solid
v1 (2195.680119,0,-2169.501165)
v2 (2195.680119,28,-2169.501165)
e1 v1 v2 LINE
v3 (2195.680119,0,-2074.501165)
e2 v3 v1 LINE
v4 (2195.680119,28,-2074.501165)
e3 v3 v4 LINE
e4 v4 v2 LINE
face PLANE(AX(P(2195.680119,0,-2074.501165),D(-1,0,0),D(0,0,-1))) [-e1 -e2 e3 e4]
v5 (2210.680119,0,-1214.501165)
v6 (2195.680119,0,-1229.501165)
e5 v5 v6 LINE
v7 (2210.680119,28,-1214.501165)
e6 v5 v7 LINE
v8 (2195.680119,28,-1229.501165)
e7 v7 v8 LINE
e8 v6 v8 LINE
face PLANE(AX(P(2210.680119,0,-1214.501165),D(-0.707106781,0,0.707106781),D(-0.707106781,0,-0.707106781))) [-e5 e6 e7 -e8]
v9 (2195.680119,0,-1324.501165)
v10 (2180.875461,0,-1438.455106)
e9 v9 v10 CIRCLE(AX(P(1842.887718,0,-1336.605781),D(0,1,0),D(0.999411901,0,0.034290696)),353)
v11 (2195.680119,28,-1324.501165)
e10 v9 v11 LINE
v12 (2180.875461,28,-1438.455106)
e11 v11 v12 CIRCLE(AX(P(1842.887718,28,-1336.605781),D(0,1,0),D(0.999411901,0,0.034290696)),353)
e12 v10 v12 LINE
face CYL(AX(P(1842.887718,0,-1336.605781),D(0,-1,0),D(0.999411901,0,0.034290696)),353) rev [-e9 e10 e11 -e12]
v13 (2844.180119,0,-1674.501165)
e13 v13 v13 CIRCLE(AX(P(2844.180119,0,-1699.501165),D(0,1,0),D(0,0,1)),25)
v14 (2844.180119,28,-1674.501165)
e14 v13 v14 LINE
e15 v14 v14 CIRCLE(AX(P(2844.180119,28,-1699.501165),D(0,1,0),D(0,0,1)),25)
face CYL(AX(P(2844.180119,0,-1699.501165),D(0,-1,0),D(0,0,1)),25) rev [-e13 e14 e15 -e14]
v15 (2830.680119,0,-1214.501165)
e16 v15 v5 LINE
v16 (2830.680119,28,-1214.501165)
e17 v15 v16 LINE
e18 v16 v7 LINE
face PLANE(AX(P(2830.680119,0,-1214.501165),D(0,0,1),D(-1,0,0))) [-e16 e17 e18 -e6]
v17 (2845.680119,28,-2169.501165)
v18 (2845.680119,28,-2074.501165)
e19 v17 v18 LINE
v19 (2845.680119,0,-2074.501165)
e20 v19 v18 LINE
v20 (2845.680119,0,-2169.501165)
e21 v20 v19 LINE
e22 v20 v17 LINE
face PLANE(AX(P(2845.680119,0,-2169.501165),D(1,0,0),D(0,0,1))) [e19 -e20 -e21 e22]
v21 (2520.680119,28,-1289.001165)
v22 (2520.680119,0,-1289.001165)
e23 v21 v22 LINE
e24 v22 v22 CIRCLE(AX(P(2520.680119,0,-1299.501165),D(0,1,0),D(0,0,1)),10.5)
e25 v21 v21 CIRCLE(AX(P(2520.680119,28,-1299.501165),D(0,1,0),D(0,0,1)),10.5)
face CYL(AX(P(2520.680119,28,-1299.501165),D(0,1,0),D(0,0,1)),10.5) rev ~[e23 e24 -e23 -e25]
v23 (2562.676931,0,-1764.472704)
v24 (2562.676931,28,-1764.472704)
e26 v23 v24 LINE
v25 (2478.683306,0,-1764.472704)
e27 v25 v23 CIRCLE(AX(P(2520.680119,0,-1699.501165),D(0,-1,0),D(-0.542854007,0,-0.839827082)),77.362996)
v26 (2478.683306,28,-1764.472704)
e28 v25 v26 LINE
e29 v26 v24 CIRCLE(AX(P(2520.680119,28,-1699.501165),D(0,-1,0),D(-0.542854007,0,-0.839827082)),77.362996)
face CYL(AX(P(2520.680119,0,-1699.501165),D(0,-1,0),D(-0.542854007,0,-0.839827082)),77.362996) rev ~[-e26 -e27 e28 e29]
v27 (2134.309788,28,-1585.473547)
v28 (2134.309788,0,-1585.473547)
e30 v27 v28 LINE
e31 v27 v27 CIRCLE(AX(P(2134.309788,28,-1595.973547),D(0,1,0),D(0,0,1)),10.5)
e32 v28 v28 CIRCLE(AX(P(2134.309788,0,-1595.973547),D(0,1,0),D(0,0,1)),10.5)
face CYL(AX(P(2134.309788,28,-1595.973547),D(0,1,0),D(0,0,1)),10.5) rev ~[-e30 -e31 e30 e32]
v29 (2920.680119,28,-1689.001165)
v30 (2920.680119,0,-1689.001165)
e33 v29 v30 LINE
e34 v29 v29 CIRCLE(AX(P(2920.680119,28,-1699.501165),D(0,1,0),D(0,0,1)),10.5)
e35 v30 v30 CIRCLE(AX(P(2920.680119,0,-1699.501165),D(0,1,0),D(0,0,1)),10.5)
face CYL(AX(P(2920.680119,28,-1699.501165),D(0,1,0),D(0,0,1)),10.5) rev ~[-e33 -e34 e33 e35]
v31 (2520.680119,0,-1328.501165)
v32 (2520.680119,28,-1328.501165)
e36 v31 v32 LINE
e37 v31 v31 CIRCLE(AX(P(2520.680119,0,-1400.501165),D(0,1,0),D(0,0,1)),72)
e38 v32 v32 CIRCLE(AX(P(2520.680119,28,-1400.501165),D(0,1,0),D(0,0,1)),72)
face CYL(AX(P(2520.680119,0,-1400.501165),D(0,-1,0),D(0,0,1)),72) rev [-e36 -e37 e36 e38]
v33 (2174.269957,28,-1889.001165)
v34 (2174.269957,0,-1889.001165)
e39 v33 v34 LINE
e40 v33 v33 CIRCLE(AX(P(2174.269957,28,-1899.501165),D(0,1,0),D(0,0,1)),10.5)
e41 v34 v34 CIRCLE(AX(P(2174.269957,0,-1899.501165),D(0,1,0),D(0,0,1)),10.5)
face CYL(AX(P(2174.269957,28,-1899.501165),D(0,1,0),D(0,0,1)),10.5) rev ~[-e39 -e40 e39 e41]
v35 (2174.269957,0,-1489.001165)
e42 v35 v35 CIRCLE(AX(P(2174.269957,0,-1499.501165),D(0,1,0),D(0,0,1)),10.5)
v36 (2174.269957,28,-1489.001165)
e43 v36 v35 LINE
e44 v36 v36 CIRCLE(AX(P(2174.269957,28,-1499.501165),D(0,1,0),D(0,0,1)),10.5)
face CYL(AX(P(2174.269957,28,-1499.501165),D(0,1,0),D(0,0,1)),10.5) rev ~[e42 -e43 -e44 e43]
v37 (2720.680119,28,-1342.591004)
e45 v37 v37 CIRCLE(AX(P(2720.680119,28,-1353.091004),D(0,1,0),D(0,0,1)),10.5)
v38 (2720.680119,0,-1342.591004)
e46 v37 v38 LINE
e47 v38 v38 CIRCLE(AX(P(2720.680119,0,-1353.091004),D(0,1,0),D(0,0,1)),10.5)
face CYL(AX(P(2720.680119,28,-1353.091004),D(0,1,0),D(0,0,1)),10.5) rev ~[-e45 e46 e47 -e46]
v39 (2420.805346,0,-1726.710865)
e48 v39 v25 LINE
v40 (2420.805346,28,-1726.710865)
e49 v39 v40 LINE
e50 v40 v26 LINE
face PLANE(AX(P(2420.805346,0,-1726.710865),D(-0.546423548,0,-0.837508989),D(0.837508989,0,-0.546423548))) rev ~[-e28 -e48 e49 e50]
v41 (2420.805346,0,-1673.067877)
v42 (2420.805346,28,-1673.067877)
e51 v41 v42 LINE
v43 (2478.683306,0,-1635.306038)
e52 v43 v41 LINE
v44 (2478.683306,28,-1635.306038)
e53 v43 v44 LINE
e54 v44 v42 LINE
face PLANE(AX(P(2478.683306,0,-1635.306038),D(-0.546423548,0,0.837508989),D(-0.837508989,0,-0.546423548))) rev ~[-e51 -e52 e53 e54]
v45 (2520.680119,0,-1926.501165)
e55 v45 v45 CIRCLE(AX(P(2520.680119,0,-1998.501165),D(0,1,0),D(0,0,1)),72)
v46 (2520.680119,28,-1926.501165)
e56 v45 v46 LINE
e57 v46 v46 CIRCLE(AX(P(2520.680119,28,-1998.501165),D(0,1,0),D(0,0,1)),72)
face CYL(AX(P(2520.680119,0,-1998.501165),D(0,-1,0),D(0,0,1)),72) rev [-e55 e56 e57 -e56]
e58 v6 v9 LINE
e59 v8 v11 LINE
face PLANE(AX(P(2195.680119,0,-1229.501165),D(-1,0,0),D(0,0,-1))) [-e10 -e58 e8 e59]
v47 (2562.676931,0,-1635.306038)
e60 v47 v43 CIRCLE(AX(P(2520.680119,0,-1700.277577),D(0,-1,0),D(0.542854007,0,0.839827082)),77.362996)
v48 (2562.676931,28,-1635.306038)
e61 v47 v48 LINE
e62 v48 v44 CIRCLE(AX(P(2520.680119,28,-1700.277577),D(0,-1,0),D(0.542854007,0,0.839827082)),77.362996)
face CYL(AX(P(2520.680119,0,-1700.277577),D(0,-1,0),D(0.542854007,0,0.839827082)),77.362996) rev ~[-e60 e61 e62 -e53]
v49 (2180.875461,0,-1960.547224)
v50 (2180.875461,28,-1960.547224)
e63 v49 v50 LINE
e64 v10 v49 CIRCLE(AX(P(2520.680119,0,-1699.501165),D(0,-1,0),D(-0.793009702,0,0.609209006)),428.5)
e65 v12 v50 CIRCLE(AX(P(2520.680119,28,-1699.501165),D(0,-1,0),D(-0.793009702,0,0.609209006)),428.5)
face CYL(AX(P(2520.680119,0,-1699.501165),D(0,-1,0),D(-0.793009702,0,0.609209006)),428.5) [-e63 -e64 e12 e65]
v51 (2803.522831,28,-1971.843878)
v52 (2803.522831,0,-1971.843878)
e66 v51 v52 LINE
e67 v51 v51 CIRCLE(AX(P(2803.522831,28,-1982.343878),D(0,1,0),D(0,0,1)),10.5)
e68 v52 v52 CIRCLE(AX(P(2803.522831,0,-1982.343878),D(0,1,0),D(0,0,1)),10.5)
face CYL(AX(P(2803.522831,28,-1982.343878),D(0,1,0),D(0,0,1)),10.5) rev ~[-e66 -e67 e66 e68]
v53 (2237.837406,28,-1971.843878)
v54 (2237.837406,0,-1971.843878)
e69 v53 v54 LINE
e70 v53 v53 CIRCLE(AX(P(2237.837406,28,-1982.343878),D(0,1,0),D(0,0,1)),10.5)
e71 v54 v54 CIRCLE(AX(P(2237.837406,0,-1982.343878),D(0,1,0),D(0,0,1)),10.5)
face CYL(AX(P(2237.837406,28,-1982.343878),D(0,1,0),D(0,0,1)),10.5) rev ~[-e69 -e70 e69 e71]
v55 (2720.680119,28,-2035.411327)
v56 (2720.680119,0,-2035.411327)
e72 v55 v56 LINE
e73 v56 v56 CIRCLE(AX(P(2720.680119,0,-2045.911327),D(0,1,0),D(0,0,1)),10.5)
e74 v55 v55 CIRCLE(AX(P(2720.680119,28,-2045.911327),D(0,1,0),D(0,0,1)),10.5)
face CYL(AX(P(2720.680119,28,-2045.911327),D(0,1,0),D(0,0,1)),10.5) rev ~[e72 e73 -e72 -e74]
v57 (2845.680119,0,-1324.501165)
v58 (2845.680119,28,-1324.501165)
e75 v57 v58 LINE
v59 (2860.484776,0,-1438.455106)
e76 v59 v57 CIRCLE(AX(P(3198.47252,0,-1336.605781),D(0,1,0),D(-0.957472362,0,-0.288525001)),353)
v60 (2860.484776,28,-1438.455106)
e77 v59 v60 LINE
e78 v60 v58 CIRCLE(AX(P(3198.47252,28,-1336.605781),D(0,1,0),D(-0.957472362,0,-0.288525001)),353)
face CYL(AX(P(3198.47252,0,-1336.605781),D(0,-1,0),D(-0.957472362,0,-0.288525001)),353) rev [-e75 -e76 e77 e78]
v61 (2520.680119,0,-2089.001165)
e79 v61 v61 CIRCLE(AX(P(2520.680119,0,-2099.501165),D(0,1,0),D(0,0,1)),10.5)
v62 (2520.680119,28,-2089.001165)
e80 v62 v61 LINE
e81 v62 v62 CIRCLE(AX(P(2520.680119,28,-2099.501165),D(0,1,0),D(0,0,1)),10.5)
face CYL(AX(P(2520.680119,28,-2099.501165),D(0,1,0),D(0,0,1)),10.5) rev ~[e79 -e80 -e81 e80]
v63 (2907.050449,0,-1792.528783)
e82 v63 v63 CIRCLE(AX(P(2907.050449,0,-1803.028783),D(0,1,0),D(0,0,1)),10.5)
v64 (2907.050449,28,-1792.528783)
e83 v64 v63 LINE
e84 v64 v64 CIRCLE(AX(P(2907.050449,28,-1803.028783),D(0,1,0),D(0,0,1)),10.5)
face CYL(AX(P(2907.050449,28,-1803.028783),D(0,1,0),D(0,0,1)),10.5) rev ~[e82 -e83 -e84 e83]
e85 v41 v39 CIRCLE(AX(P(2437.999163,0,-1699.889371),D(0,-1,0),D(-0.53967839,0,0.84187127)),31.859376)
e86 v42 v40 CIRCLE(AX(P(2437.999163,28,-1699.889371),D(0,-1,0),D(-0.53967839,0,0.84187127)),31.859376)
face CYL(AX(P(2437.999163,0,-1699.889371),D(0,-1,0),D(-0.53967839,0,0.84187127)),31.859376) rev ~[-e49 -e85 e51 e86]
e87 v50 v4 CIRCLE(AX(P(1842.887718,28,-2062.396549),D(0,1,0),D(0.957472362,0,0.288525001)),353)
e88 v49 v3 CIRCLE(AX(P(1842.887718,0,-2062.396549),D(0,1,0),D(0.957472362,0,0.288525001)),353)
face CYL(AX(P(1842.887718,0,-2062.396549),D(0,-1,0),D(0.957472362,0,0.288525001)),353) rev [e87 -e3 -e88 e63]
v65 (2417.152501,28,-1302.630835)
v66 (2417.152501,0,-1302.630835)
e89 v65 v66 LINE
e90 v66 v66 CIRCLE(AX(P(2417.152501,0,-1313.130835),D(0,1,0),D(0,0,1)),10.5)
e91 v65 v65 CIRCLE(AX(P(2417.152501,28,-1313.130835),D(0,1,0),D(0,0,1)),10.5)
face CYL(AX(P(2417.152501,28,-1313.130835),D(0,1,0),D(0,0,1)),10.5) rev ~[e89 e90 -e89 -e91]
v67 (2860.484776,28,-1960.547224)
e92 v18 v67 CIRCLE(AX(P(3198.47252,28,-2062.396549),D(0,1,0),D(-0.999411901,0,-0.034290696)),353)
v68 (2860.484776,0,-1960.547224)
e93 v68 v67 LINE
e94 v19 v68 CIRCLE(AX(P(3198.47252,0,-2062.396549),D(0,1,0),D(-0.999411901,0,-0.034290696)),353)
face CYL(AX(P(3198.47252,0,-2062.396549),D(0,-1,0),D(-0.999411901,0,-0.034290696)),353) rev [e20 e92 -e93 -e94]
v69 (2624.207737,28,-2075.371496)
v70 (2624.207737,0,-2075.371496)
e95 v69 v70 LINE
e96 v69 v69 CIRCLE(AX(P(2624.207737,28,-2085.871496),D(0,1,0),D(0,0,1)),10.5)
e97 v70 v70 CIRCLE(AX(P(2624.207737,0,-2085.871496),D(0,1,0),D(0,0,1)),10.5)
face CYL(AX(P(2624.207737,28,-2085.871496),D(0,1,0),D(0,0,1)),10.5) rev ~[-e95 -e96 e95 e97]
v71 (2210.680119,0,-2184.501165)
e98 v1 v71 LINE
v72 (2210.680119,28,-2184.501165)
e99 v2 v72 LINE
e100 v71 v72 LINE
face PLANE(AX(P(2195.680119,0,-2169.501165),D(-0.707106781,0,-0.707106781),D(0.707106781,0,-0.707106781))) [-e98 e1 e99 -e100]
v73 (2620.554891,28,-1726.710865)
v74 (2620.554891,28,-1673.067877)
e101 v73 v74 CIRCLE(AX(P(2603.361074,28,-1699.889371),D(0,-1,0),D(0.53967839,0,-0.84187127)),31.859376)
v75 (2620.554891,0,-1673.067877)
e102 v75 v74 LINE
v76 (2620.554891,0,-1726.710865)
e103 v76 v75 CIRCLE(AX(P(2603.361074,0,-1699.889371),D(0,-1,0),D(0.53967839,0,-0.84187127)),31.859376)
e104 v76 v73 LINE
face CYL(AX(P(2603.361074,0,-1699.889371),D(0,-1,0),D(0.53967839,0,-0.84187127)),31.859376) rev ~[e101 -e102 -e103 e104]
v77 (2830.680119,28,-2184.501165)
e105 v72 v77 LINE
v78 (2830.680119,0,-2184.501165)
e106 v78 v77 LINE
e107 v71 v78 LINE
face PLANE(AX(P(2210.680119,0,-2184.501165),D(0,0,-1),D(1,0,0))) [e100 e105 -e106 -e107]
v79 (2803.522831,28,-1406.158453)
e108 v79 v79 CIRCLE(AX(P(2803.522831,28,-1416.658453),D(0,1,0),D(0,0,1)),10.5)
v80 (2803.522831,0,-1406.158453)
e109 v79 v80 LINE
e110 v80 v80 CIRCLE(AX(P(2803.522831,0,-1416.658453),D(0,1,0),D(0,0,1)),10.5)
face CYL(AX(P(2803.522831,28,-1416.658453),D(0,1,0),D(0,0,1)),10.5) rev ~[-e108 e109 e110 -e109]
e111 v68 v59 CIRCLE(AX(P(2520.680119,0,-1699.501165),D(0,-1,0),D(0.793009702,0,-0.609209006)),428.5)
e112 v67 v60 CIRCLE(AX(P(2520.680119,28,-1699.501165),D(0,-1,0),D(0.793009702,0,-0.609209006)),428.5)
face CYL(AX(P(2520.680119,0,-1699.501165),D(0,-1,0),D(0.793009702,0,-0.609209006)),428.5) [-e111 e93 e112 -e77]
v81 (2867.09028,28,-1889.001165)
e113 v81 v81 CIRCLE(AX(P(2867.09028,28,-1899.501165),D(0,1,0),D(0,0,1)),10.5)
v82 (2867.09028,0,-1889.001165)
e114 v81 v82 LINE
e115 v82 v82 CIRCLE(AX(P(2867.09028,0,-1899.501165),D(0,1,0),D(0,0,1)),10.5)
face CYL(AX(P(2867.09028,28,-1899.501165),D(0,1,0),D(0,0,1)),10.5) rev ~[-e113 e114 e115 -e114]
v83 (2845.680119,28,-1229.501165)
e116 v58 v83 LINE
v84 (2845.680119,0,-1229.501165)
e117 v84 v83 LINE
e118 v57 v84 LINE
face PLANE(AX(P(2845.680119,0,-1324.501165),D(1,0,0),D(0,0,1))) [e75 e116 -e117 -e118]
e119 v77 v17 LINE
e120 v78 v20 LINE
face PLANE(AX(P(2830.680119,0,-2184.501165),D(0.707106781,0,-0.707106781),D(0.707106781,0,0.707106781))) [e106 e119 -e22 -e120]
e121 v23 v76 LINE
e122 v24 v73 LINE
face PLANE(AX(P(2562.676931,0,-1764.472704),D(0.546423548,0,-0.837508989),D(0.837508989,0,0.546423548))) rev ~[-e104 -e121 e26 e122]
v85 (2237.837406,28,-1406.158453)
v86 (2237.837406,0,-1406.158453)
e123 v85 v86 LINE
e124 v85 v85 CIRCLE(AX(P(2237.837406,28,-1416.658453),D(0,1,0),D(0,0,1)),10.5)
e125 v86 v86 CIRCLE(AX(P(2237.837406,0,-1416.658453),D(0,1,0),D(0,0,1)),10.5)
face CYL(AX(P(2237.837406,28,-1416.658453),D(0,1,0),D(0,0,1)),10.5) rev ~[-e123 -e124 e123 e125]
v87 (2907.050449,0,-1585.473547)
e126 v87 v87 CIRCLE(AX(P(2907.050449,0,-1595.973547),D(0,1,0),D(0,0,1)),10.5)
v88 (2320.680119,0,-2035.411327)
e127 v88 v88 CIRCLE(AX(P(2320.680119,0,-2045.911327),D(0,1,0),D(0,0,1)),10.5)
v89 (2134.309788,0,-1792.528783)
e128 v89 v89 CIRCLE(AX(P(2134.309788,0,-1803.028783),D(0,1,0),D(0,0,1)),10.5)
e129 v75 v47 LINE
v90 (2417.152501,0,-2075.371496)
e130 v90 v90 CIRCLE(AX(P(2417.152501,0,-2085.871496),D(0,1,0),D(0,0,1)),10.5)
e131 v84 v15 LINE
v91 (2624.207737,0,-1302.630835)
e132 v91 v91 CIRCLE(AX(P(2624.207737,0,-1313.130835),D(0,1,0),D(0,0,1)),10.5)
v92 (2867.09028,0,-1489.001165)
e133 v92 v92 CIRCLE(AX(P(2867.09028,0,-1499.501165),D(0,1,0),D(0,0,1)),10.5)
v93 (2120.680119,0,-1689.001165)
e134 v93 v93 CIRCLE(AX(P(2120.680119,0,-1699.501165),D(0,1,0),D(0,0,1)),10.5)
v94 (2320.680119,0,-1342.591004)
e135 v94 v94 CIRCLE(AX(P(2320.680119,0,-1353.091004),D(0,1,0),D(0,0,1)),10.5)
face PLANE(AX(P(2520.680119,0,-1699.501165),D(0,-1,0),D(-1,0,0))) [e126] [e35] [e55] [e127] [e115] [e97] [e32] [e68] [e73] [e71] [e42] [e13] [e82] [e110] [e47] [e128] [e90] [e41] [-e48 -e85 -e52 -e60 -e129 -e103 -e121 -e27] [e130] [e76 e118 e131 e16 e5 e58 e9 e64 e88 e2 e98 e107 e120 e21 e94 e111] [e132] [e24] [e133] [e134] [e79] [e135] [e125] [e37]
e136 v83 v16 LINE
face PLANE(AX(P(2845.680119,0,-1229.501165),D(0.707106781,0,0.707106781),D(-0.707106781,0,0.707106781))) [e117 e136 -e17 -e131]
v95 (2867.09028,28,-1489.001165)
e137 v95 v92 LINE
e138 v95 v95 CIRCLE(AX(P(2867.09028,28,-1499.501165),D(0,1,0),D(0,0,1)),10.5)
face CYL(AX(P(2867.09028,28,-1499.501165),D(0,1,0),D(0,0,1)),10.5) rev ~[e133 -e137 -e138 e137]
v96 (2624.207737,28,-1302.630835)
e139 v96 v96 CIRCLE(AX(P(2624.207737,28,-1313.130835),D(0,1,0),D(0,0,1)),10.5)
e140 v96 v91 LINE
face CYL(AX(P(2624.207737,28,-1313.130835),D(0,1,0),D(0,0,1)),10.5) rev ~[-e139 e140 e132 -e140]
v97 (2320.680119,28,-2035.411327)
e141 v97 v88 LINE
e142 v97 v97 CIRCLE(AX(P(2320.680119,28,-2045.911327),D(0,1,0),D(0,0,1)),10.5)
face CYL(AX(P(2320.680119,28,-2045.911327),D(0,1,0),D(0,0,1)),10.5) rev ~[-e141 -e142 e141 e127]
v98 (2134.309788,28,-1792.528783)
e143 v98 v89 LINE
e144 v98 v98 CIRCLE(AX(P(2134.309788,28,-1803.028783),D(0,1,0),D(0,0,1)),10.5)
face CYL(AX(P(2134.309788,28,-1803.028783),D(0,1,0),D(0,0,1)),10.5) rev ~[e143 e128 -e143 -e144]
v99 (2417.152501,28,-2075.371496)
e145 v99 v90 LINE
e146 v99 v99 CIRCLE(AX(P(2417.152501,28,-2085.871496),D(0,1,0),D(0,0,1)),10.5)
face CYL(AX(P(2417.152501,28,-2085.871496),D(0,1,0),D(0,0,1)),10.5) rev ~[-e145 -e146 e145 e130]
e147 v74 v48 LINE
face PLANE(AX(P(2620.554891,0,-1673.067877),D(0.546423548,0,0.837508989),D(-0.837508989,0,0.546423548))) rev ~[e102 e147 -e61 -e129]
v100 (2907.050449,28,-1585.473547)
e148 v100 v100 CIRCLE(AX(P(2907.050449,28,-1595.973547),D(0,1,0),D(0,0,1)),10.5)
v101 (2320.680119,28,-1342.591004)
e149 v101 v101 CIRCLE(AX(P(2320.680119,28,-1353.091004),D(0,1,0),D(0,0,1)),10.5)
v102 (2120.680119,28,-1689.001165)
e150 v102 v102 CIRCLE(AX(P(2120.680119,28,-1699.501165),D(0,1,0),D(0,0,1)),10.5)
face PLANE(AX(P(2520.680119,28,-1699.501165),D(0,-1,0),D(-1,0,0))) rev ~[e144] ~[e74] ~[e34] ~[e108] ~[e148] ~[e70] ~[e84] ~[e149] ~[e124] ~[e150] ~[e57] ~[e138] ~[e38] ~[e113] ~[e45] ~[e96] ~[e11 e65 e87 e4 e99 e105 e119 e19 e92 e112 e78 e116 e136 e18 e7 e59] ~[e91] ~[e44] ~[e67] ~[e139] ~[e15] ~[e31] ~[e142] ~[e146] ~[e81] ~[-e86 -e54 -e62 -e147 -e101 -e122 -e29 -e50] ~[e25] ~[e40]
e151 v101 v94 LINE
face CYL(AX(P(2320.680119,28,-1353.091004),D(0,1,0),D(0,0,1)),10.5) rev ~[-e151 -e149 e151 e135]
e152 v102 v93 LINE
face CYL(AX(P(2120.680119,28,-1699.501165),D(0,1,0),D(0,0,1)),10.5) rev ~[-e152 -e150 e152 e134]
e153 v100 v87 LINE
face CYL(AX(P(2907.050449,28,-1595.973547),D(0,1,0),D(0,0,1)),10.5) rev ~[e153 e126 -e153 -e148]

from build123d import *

# Parameters (mm, degrees)
SKETCH3_R           = 25
SKETCH3_R_2         = 72
BOSS_EXTRUDE1_DEPTH = 28
SKETCH4_R           = 10.5
CUT_EXTRUDE1_DEPTH  = 3671.216984417


with BuildPart() as part:
    # Sketch3 → Boss-Extrude1 (new body)
    with BuildSketch(Plane(origin=(0, 0, 0), x_dir=(1, 0, 0), z_dir=(0, 1, 0))):
        with BuildLine():
            Line((2845.680118699, 2169.501165066), (2845.680118699, 2074.501165066))
            ThreePointArc((2845.680118699, 2074.501165066), (2848.414414178, 2016.917733414), (2860.484776028, 1960.547223948))
            ThreePointArc((2860.484776028, 1960.547223948), (2949.180118699, 1699.501165066), (2860.484776028, 1438.455106185))
            ThreePointArc((2860.484776028, 1438.455106185), (2848.414414178, 1382.084596719), (2845.680118699, 1324.501165066))
            Line((2845.680118699, 1324.501165066), (2845.680118699, 1229.501165066))
            Line((2845.680118699, 1229.501165066), (2830.680118699, 1214.501165066))
            Line((2830.680118699, 1214.501165066), (2210.680118699, 1214.501165066))
            Line((2210.680118699, 1214.501165066), (2195.680118699, 1229.501165066))
            Line((2195.680118699, 1229.501165066), (2195.680118699, 1324.501165066))
            ThreePointArc((2195.680118699, 1324.501165066), (2192.94582322, 1382.084596719), (2180.87546137, 1438.455106185))
            ThreePointArc((2180.87546137, 1438.455106185), (2092.180118699, 1699.501165066), (2180.87546137, 1960.547223948))
            ThreePointArc((2180.87546137, 1960.547223948), (2192.94582322, 2016.917733414), (2195.680118699, 2074.501165066))
            Line((2195.680118699, 2074.501165066), (2195.680118699, 2169.501165066))
            Line((2195.680118699, 2169.501165066), (2210.680118699, 2184.501165066))
            Line((2210.680118699, 2184.501165066), (2830.680118699, 2184.501165066))
            Line((2830.680118699, 2184.501165066), (2845.680118699, 2169.501165066))
        make_face()
        with Locations(Location((2844.180118699, 1699.501165066, 0), (0, 0, 270))):
            Circle(SKETCH3_R, mode=Mode.SUBTRACT)
        with Locations(Location((2520.680118699, 1400.501165066, 0), (0, 0, 270))):
            Circle(SKETCH3_R_2, mode=Mode.SUBTRACT)
        with Locations(Location((2520.680118699, 1998.501165066, 0), (0, 0, 270))):
            Circle(SKETCH3_R_2, mode=Mode.SUBTRACT)
        with BuildLine():
            Line((2620.554891012, 1673.06787727), (2562.676931085, 1635.306037562))
            ThreePointArc((2562.676931085, 1635.306037562), (2520.680118699, 1622.914580714), (2478.683306313, 1635.306037562))
            Line((2478.683306313, 1635.306037562), (2420.805346386, 1673.06787727))
            ThreePointArc((2420.805346386, 1673.06787727), (2406.139786968, 1699.889370895), (2420.805346386, 1726.71086452))
            Line((2420.805346386, 1726.71086452), (2478.683306313, 1764.472704228))
            ThreePointArc((2478.683306313, 1764.472704228), (2520.680118699, 1776.864161076), (2562.676931085, 1764.472704228))
            Line((2562.676931085, 1764.472704228), (2620.554891012, 1726.71086452))
            ThreePointArc((2620.554891012, 1726.71086452), (2635.220450429, 1699.889370895), (2620.554891012, 1673.06787727))
        make_face(mode=Mode.SUBTRACT)
    extrude(amount=BOSS_EXTRUDE1_DEPTH)

    # Sketch4 → Cut-Extrude1 (cut, through all)
    with BuildSketch(Plane(origin=(0, 28, 0), x_dir=(1, 0, 0), z_dir=(0, 1, 0))):
        with Locations(Location((2520.680118699, 2099.501165066, 0), (0, 0, 270))):
            Circle(SKETCH4_R)
        with Locations(Location((2624.20773674, 2085.871495582, 0), (0, 0, 270))):
            Circle(SKETCH4_R)
        with Locations(Location((2720.680118699, 2045.91132658, 0), (0, 0, 270))):
            Circle(SKETCH4_R)
        with Locations(Location((2803.522831173, 1982.343877541, 0), (0, 0, 270))):
            Circle(SKETCH4_R)
        with Locations(Location((2867.090280213, 1899.501165066, 0), (0, 0, 270))):
            Circle(SKETCH4_R)
        with Locations(Location((2907.050449214, 1803.028783107, 0), (0, 0, 270))):
            Circle(SKETCH4_R)
        with Locations(Location((2920.680118699, 1699.501165066, 0), (0, 0, 270))):
            Circle(SKETCH4_R)
        with Locations(Location((2907.050449214, 1595.973547025, 0), (0, 0, 270))):
            Circle(SKETCH4_R)
        with Locations(Location((2867.090280213, 1499.501165066, 0), (0, 0, 270))):
            Circle(SKETCH4_R)
        with Locations(Location((2803.522831173, 1416.658452592, 0), (0, 0, 270))):
            Circle(SKETCH4_R)
        with Locations(Location((2720.680118699, 1353.091003552, 0), (0, 0, 270))):
            Circle(SKETCH4_R)
        with Locations(Location((2624.20773674, 1313.130834551, 0), (0, 0, 270))):
            Circle(SKETCH4_R)
        with Locations(Location((2520.680118699, 1299.501165066, 0), (0, 0, 270))):
            Circle(SKETCH4_R)
        with Locations(Location((2417.152500658, 1313.130834551, 0), (0, 0, 270))):
            Circle(SKETCH4_R)
        with Locations(Location((2320.680118699, 1353.091003552, 0), (0, 0, 270))):
            Circle(SKETCH4_R)
        with Locations(Location((2237.837406224, 1416.658452592, 0), (0, 0, 270))):
            Circle(SKETCH4_R)
        with Locations(Location((2174.269957185, 1499.501165066, 0), (0, 0, 270))):
            Circle(SKETCH4_R)
        with Locations(Location((2134.309788183, 1595.973547025, 0), (0, 0, 270))):
            Circle(SKETCH4_R)
        with Locations(Location((2120.680118699, 1699.501165066, 0), (0, 0, 270))):
            Circle(SKETCH4_R)
        with Locations(Location((2134.309788183, 1803.028783107, 0), (0, 0, 270))):
            Circle(SKETCH4_R)
        with Locations(Location((2174.269957185, 1899.501165066, 0), (0, 0, 270))):
            Circle(SKETCH4_R)
        with Locations(Location((2237.837406224, 1982.343877541, 0), (0, 0, 270))):
            Circle(SKETCH4_R)
        with Locations(Location((2320.680118699, 2045.91132658, 0), (0, 0, 270))):
            Circle(SKETCH4_R)
        with Locations(Location((2417.152500658, 2085.871495582, 0), (0, 0, 270))):
            Circle(SKETCH4_R)
    extrude(amount=-CUT_EXTRUDE1_DEPTH, mode=Mode.SUBTRACT)


solid = part.part
